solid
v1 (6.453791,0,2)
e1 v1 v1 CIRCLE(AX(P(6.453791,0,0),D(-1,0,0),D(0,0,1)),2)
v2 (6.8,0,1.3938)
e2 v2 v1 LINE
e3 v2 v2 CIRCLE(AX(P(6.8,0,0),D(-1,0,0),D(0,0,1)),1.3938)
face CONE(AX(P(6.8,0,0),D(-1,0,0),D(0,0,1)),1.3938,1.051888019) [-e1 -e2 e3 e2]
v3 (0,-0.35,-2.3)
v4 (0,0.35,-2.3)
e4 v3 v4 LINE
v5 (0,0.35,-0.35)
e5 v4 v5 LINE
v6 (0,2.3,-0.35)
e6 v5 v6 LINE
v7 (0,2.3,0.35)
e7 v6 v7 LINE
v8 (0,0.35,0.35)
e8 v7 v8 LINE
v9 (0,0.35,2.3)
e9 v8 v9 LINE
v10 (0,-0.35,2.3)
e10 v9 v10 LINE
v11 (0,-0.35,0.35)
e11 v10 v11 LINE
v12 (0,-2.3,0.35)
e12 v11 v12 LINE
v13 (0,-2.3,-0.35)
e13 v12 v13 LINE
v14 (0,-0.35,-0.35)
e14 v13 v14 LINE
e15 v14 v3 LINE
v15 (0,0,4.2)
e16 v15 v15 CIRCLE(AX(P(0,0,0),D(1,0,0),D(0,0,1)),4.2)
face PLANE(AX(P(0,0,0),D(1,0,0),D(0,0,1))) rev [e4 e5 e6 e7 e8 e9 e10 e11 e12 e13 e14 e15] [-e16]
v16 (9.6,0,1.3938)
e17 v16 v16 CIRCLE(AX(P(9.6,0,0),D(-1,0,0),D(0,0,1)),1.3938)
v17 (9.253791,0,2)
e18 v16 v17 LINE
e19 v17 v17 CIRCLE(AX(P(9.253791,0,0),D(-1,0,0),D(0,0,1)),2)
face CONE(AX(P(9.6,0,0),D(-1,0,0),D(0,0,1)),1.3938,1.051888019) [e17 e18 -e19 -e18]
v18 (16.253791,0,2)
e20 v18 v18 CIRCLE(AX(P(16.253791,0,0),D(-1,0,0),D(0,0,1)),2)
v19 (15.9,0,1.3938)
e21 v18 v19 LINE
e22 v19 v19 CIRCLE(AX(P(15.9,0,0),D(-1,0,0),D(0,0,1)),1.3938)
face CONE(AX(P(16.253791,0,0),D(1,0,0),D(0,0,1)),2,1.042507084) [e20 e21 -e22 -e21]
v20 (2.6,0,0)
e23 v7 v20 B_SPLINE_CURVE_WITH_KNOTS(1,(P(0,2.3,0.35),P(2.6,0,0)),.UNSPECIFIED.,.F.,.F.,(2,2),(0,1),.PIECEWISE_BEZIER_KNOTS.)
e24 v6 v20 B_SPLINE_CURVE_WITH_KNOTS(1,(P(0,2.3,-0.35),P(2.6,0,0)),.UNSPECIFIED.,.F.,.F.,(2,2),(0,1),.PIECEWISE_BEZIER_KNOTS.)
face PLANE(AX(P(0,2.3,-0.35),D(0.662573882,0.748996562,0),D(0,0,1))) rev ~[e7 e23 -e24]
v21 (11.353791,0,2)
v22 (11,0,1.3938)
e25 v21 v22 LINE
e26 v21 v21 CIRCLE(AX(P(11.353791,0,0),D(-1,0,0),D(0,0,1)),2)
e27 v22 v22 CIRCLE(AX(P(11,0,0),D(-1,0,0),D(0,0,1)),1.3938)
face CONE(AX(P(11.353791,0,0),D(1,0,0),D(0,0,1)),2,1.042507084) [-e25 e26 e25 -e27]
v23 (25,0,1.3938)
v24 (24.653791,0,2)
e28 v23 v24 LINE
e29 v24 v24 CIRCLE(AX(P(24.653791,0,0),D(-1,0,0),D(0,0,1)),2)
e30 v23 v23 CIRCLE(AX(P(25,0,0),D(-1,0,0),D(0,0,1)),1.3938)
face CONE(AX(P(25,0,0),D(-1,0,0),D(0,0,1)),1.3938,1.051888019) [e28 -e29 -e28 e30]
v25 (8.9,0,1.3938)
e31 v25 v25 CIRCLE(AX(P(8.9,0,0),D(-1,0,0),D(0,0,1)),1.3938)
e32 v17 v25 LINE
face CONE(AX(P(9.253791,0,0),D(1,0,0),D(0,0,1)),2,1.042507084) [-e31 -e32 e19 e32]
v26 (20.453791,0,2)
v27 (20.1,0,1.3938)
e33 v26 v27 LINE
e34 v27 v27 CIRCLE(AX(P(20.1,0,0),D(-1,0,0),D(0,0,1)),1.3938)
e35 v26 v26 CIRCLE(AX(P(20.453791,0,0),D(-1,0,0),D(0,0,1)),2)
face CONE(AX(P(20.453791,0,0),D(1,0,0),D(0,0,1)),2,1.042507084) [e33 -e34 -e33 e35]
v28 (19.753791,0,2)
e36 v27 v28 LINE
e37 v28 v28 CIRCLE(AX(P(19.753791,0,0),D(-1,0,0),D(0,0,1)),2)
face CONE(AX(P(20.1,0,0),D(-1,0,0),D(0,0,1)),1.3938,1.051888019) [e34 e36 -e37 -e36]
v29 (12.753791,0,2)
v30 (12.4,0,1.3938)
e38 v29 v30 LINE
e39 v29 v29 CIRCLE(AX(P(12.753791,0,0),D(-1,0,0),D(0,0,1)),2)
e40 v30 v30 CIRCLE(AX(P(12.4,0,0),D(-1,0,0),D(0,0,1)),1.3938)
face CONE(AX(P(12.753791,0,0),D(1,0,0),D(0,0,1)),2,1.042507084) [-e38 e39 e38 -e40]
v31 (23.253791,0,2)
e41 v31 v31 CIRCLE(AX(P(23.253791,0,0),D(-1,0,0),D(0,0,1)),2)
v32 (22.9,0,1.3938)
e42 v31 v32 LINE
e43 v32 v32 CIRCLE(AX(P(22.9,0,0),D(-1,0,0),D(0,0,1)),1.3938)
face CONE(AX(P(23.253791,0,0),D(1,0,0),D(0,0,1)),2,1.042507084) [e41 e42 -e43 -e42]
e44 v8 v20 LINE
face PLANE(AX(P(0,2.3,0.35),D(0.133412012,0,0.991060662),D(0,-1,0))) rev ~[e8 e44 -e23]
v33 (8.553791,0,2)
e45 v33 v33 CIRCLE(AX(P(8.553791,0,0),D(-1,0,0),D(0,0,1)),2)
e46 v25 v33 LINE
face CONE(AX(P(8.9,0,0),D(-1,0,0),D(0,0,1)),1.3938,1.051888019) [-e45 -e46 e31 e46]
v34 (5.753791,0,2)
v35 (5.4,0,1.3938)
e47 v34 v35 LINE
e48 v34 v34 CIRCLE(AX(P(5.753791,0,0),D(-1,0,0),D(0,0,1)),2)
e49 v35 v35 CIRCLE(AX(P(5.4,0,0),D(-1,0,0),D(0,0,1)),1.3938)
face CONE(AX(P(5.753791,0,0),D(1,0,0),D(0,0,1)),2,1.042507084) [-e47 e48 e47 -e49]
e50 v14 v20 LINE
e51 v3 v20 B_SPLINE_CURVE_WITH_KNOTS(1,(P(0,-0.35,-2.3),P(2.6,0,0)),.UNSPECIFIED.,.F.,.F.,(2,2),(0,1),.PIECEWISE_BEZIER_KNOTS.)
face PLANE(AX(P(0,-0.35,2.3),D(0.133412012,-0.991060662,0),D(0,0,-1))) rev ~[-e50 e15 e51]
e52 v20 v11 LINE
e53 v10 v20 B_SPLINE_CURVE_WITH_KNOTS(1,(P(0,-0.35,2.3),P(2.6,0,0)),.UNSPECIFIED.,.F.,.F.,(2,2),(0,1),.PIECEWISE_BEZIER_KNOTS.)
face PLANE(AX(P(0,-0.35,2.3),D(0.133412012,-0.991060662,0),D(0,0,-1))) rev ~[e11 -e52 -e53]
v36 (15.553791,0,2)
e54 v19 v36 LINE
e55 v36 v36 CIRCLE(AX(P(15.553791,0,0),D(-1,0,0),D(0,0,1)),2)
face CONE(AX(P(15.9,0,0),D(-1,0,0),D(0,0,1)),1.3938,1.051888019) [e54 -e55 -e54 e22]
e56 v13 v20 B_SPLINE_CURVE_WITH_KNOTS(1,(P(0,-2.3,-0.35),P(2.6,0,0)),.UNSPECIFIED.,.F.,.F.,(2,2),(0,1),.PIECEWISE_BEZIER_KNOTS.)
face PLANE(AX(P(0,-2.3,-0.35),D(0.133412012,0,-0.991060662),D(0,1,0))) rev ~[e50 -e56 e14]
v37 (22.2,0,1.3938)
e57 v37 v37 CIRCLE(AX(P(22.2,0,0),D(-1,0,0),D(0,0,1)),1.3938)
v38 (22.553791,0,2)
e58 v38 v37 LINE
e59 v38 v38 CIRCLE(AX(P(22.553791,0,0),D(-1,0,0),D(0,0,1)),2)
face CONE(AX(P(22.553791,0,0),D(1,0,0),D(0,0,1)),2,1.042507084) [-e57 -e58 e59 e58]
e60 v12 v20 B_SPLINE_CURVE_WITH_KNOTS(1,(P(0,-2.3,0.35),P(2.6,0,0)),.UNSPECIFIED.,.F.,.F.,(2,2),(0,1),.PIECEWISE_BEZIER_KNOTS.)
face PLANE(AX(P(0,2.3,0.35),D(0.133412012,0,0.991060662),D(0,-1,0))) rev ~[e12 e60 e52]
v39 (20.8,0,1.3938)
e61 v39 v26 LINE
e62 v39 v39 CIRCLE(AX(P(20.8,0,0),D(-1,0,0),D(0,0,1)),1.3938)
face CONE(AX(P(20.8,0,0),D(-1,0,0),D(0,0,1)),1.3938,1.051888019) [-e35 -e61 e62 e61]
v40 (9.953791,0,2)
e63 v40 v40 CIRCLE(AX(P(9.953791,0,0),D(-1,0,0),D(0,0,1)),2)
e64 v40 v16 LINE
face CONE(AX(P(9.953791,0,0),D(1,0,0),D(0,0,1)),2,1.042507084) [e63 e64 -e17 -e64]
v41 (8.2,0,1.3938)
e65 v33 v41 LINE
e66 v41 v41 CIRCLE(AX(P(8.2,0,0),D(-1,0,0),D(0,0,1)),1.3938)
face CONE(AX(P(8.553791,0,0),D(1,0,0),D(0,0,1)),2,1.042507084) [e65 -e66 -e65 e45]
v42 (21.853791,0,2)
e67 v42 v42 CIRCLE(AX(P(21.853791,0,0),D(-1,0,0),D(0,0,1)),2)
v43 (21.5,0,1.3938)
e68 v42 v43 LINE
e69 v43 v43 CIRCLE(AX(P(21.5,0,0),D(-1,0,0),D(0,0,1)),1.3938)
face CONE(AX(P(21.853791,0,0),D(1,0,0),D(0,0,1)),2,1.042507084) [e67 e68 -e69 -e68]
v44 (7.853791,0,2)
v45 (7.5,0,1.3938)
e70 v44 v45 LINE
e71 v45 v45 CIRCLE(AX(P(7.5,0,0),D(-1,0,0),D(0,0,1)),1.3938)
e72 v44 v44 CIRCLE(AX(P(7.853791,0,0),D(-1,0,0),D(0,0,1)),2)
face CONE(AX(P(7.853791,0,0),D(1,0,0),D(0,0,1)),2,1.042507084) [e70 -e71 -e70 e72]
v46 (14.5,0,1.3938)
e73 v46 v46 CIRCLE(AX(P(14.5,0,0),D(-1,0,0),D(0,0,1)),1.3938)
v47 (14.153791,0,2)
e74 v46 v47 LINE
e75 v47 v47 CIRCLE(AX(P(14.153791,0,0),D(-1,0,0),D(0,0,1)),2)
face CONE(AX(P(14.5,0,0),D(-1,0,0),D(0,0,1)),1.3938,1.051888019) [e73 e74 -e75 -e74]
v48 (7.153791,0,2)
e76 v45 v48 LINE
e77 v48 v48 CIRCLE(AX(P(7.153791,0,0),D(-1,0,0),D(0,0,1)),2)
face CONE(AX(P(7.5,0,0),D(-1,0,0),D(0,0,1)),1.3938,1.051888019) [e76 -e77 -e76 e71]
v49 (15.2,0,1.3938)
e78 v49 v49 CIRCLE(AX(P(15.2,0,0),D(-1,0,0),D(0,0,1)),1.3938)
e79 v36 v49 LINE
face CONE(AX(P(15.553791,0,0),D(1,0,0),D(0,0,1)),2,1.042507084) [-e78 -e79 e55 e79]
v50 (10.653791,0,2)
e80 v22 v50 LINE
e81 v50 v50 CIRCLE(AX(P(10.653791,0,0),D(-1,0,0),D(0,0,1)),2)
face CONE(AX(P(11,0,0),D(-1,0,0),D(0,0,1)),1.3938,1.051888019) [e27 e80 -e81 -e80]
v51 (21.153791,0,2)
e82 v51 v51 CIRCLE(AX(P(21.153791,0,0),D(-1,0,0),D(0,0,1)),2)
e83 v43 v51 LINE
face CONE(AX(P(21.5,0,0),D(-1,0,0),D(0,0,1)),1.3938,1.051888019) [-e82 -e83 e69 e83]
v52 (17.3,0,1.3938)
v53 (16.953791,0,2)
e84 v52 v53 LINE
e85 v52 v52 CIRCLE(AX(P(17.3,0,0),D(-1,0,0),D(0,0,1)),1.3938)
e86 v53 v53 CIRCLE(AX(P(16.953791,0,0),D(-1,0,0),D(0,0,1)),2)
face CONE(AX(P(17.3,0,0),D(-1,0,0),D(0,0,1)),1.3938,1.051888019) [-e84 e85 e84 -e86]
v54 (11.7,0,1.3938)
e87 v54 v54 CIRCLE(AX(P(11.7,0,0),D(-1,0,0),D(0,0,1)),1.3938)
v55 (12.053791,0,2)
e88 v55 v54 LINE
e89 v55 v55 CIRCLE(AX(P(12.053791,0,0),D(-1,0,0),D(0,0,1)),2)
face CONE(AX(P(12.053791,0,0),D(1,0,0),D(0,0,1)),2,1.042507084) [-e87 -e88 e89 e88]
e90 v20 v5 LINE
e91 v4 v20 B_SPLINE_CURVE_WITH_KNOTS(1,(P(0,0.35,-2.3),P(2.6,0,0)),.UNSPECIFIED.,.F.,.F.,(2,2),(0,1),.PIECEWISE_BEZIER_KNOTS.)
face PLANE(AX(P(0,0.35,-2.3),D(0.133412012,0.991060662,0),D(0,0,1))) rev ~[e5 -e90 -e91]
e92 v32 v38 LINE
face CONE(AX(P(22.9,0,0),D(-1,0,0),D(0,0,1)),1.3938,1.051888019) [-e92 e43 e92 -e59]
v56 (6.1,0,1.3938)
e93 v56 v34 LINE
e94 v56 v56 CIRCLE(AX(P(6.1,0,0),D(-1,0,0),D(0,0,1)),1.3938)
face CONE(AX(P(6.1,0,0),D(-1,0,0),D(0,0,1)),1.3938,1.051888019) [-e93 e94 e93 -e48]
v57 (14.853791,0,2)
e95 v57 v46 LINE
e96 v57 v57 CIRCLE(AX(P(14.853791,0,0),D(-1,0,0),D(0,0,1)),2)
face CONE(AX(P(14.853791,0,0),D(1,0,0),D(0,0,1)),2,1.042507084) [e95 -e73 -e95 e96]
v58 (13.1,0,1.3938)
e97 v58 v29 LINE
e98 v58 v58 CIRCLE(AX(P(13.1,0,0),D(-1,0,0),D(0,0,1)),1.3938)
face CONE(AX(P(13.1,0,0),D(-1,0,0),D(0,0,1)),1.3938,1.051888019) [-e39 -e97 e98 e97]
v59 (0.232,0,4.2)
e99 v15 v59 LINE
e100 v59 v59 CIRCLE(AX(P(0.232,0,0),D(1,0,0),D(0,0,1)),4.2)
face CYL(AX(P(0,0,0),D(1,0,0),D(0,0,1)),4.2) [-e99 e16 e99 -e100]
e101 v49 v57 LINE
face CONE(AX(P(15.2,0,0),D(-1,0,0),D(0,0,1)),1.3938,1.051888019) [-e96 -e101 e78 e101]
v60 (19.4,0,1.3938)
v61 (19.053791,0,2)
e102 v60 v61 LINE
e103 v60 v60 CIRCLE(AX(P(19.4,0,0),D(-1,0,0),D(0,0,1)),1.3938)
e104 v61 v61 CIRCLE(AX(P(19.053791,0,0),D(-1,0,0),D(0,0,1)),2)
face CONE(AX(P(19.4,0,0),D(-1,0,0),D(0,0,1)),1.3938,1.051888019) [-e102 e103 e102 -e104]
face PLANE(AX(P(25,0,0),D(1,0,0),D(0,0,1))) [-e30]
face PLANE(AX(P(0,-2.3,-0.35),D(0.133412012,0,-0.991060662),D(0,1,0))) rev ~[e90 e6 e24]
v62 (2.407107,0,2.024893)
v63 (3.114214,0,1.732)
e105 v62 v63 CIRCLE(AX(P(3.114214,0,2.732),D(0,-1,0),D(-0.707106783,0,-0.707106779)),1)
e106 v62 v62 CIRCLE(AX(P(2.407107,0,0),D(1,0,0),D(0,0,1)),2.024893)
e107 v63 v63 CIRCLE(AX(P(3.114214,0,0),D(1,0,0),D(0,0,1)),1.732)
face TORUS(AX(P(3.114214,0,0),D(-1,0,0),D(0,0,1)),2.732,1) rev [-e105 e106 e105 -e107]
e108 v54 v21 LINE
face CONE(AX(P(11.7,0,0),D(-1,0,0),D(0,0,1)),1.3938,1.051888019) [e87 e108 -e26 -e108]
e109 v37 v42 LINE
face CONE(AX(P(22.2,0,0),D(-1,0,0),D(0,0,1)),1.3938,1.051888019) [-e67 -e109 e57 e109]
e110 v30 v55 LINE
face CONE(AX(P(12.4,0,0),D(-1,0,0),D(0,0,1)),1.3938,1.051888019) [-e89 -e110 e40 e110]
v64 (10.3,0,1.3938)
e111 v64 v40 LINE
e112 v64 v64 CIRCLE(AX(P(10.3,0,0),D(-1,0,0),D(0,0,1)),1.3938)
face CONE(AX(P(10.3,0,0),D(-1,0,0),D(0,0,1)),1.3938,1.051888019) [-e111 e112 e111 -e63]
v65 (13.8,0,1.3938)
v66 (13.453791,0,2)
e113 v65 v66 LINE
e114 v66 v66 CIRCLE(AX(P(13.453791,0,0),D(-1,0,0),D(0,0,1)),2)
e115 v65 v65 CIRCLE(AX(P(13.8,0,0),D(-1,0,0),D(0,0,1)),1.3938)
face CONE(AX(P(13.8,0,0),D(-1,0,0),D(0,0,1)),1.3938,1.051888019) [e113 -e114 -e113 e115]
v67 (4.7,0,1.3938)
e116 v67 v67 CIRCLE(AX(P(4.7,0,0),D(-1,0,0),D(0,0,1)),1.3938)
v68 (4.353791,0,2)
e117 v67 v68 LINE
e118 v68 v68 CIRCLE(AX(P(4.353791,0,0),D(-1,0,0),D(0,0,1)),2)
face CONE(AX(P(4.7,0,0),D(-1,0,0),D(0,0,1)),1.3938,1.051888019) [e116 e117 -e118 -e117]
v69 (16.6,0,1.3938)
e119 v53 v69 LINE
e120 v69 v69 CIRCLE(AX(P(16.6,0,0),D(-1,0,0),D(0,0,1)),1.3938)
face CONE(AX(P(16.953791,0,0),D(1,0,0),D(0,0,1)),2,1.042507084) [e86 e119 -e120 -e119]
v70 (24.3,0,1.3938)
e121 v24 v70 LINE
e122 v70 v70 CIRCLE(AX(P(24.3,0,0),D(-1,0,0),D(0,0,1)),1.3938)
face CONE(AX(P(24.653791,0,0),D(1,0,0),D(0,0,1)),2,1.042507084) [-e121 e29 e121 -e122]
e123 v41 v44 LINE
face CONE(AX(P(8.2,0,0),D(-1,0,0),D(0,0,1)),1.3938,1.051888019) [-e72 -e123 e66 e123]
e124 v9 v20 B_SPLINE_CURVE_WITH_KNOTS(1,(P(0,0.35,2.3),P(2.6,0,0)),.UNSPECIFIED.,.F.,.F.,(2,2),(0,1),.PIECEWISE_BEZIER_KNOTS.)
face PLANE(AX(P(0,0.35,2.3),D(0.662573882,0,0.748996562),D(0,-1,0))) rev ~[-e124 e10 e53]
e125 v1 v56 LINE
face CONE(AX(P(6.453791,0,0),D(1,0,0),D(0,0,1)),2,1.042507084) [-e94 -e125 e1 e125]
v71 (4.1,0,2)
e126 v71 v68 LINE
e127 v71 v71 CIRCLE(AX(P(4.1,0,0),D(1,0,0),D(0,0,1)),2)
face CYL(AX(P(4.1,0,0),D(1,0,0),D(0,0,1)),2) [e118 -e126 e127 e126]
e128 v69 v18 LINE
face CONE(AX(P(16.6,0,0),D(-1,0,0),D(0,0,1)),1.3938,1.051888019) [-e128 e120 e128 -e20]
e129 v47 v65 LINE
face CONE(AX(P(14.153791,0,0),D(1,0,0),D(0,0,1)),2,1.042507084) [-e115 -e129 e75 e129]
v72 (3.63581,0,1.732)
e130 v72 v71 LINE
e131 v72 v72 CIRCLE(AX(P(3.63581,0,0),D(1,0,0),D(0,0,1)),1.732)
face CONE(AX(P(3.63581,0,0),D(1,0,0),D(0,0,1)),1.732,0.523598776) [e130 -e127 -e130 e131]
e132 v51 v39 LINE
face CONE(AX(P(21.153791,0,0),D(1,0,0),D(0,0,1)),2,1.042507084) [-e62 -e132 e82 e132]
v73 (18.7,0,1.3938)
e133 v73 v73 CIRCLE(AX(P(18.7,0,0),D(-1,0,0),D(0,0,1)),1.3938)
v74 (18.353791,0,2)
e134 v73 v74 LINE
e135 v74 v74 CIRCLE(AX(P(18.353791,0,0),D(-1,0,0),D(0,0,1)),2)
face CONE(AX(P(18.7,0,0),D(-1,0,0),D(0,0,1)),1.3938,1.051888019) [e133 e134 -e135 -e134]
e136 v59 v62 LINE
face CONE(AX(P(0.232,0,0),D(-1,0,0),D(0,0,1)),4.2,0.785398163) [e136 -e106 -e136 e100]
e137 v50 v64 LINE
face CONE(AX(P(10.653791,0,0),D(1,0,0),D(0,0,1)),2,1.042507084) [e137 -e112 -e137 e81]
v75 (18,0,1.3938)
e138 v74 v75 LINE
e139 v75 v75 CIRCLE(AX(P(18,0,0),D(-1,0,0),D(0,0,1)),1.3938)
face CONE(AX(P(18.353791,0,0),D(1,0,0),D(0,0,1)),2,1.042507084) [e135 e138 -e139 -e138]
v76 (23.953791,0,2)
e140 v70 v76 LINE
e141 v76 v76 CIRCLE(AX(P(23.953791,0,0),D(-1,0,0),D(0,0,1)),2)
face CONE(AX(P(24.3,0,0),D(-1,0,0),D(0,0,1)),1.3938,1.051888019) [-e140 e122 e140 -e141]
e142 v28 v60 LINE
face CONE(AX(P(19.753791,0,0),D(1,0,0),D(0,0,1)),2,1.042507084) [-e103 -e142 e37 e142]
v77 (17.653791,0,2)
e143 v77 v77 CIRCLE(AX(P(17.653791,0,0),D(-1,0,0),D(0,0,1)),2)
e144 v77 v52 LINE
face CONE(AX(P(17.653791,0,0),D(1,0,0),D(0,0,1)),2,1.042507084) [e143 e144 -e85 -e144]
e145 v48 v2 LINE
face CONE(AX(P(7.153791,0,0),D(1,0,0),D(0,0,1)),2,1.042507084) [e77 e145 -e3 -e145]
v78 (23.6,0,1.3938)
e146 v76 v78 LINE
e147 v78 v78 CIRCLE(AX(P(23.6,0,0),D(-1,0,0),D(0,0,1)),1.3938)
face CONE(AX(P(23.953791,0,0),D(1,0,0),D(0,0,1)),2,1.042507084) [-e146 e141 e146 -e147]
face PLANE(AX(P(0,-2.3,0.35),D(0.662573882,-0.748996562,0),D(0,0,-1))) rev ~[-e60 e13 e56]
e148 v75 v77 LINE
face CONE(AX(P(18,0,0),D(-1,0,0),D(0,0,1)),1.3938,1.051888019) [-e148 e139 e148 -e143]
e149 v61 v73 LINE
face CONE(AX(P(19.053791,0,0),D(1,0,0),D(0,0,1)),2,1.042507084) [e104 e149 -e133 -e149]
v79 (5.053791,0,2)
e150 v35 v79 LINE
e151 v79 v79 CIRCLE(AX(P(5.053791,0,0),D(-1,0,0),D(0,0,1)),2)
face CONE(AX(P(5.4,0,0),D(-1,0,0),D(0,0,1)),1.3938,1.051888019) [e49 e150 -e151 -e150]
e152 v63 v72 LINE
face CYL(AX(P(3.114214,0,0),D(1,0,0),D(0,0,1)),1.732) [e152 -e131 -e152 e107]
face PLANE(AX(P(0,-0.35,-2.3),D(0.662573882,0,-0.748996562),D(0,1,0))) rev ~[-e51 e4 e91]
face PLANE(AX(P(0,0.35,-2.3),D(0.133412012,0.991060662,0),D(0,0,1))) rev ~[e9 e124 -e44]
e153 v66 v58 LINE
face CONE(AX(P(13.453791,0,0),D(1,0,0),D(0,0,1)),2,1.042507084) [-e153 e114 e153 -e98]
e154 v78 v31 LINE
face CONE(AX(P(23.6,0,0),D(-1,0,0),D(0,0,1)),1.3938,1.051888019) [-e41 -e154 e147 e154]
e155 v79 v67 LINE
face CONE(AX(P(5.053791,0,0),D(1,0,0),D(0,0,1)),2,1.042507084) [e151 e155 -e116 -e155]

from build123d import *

# Parameters (mm, degrees)
PATTERN_LINEAR_1_COUNT   = 30
PATTERN_LINEAR_1_PITCH   = 0.7
PATTERN_CIRCULAR_1_COUNT = 2
PATTERN_CIRCULAR_1_ANGLE = 90


with BuildPart() as part:
    # 草图1 → Revolve 689 (revolve)
    with BuildSketch(Plane.XY, mode=Mode.PRIVATE) as revolve_689_sk:
        with BuildLine():
            Line((0, 0), (0, 4.2))
            Line((0, 4.2), (0.232, 4.2))
            Line((0.232, 4.2), (2.407106781, 2.024893219))
            ThreePointArc((2.407106781, 2.024893219), (2.73153013, 1.808120467), (3.114213562, 1.732))
            Line((3.114213562, 1.732), (3.635810384, 1.732))
            Line((3.635810384, 1.732), (4.1, 2))
            Line((4.1, 2), (25, 2))
            Line((25, 2), (25, 0))
            Line((25, 0), (0, 0))
        make_face()
    revolve(revolve_689_sk.sketch.rotate(Axis((0, 0, 0), (1, 0, 0)), 90), axis=Axis((0, 0, 0), (1, 0, 0)))

    # 草图2 → 切除-旋转1 (revolve, cut)
    with BuildSketch(Plane.XY, mode=Mode.PRIVATE) as cut_revolve_1_sk:
        Polygon((24.653791204, 2), (25.353791204, 2), (25, 1.3938), align=None)
    cut_revolve_1 = revolve(cut_revolve_1_sk.sketch.rotate(Axis((0, 0, 0), (-1, 0, 0)), 270), axis=Axis((0, 0, 0), (-1, 0, 0)), mode=Mode.SUBTRACT)

    # 阵列(线性)1: 切除-旋转1 ×30
    with Locations(*[(-i * PATTERN_LINEAR_1_PITCH, 0, 0) for i in range(1, PATTERN_LINEAR_1_COUNT)]):
        add(cut_revolve_1, mode=Mode.SUBTRACT)

    # 草图3 → 切除-放样1 section 0
    with BuildSketch(Plane.ZY, mode=Mode.PRIVATE) as loft_1_s0:
        with BuildLine():
            Line((-2.3, 0.35), (2.3, 0.35))
            Line((2.3, 0.35), (2.3, -0.35))
            Line((2.3, -0.35), (-2.3, -0.35))
            Line((-2.3, -0.35), (-2.3, 0.35))
        make_face()
    loft_1 = loft([loft_1_s0.sketch, Vertex(2.6, 0, 0)], mode=Mode.SUBTRACT)

    # 阵列(圆周)1: 切除-放样1 ×2 about axis
    pattern_circular_1_axis = Axis((0, 0, 0), (1, 0, 0))
    for i in range(1, PATTERN_CIRCULAR_1_COUNT):
        add(loft_1.rotate(pattern_circular_1_axis, i * PATTERN_CIRCULAR_1_ANGLE / (PATTERN_CIRCULAR_1_COUNT - 1)), mode=Mode.SUBTRACT)


solid = part.part
